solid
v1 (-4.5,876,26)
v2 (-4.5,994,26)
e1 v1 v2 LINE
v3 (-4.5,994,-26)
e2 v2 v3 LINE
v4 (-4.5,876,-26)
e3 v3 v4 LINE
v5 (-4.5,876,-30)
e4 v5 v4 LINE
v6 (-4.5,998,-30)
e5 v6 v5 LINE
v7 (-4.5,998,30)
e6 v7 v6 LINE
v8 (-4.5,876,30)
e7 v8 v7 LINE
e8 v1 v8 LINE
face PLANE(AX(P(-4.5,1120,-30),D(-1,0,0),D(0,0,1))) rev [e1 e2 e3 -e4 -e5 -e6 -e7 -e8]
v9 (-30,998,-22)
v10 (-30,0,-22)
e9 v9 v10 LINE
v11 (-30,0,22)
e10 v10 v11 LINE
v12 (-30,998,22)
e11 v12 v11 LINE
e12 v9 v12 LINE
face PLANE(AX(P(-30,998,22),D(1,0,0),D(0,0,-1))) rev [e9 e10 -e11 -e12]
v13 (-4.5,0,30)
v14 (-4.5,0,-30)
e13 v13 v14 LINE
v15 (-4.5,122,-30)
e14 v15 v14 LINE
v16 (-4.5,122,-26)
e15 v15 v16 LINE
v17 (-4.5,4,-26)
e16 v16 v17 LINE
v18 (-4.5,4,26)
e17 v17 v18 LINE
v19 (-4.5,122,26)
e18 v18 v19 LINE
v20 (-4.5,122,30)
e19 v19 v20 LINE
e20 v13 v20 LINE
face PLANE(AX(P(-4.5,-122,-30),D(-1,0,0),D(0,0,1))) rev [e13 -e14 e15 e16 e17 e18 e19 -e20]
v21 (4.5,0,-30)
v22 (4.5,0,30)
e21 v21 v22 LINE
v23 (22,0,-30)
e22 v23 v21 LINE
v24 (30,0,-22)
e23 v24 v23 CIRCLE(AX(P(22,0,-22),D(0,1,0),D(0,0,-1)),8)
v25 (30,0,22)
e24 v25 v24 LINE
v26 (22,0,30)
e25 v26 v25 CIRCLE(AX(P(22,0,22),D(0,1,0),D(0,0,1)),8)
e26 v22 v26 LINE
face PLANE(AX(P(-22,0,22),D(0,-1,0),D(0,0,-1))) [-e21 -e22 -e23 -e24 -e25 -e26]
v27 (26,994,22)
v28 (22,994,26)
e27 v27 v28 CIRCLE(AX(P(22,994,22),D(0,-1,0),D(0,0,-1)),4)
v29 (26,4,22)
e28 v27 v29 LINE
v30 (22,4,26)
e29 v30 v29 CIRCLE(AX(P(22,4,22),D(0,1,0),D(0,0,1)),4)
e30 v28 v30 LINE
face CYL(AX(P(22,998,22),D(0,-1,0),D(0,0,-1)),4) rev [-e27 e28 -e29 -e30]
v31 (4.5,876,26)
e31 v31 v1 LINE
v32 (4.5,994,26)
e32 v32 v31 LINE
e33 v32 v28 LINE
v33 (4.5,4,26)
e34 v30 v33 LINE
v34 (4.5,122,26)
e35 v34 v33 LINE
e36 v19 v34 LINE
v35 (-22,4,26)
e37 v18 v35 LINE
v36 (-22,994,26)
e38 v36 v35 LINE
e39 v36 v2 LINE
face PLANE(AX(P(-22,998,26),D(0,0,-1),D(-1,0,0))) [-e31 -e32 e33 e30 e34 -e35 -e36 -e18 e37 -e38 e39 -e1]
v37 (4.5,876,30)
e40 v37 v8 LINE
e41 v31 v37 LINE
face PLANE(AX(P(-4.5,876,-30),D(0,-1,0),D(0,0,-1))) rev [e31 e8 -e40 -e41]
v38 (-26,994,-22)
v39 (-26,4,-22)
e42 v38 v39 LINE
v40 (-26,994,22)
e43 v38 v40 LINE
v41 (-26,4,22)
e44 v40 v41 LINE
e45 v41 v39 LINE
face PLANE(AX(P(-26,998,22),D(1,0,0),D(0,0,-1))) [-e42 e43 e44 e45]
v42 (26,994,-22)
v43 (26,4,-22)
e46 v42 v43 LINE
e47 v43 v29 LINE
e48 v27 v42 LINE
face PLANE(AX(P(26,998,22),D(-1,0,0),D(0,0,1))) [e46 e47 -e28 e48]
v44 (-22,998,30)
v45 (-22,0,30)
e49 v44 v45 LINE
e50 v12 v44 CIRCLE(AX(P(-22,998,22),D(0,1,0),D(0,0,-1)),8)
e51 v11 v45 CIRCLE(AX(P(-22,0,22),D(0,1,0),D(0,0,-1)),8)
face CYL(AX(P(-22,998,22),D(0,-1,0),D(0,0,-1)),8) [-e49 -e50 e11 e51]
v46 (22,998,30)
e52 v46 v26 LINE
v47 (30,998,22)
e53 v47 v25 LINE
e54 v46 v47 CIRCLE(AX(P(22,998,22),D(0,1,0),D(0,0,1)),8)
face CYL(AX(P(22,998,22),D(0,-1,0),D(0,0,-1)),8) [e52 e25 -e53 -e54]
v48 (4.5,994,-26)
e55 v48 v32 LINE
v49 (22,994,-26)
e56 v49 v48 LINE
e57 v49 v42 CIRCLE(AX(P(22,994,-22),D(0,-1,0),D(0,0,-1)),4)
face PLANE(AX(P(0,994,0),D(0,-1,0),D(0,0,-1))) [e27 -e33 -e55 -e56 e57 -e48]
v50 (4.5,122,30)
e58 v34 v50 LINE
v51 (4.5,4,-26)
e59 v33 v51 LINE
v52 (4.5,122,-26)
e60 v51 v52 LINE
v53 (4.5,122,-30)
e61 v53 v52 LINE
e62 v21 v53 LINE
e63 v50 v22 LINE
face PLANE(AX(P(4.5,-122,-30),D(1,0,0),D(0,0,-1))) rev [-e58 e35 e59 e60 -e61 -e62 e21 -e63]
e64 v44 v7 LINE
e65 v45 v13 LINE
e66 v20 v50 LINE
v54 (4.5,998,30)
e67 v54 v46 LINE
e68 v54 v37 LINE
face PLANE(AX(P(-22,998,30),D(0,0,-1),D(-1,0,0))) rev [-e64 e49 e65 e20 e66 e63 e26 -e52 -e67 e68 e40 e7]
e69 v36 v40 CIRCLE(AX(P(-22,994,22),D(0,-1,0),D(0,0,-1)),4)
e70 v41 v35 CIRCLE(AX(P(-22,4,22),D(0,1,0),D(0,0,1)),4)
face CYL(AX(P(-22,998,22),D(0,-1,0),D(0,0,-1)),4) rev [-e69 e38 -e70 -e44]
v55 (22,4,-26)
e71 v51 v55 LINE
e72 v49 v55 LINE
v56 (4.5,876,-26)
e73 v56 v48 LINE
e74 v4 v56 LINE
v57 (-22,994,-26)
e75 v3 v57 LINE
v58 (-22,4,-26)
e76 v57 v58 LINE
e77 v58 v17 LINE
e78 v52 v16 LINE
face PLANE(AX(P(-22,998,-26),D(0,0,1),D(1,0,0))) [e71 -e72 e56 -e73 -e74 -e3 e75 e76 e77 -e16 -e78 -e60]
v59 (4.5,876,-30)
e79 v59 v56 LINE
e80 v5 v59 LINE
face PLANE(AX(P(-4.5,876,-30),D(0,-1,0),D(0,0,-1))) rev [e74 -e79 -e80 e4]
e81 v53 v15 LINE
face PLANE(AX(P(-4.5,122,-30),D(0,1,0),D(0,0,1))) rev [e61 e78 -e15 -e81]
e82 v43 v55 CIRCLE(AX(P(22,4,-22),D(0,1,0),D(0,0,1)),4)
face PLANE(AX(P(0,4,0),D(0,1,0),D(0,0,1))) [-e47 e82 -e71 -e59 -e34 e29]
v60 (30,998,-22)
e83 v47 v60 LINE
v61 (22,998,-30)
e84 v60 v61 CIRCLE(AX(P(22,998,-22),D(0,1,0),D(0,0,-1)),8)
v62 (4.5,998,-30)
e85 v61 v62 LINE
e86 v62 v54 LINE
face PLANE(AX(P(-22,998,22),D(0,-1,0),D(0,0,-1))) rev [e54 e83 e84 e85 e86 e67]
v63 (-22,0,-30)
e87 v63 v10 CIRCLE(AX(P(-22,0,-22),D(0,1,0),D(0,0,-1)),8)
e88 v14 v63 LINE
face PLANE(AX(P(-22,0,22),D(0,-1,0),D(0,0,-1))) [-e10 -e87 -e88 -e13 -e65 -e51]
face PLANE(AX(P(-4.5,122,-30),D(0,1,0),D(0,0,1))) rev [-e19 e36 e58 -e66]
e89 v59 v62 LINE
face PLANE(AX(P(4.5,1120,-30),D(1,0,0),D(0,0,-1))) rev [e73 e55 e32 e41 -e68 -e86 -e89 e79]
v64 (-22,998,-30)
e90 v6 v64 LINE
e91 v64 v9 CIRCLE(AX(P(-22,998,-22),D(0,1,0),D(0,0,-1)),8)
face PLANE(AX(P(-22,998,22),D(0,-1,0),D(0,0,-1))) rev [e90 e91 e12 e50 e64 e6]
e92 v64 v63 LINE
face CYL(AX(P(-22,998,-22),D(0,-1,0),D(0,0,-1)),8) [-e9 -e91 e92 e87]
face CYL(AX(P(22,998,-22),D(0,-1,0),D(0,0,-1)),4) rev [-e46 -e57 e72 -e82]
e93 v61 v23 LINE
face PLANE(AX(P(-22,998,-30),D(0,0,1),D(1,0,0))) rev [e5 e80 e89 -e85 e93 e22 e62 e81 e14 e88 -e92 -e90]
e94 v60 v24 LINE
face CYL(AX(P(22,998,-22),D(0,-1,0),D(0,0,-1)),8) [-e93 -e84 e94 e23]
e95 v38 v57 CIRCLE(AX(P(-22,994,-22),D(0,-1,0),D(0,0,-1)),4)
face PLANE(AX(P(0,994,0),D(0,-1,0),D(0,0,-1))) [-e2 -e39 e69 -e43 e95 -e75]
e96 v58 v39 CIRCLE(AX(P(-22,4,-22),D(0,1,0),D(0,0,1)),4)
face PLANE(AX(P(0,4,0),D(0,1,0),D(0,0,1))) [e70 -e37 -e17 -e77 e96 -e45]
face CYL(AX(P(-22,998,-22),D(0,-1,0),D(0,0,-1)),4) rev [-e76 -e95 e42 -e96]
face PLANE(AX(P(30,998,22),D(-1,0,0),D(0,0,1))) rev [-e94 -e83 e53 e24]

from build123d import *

# Parameters (mm, degrees)
BOSS_EXTRUDE1_DEPTH     = 998
CUT_EXTRUDE1_DEPTH      = 1001.251968256
CUT_EXTRUDE1_DEPTH_BACK = 1001.251968256
SKETCH2_W               = 9
SKETCH2_H               = 244
SKETCH3_W               = 21.5
SKETCH3_H               = 52
BOSS_EXTRUDE2_DEPTH     = 4
SKETCH4_W               = 21.5
SKETCH4_H               = 52
BOSS_EXTRUDE3_DEPTH     = 4


with BuildPart() as part:
    # Sketch1 → Boss-Extrude1 (new body)
    with BuildSketch(Plane(origin=(0, 0, 0), x_dir=(1, 0, 0), z_dir=(0, 1, 0))):
        with BuildLine():
            Line((-22, -30), (22, -30))
            ThreePointArc((22, -30), (27.656854249, -27.656854249), (30, -22))
            Line((30, -22), (30, 22))
            ThreePointArc((30, 22), (27.656854249, 27.656854249), (22, 30))
            Line((22, 30), (-22, 30))
            ThreePointArc((-22, 30), (-27.656854249, 27.656854249), (-30, 22))
            Line((-30, 22), (-30, -22))
            ThreePointArc((-30, -22), (-27.656854249, -27.656854249), (-22, -30))
        make_face()
        with BuildLine():
            Line((-22, 26), (22, 26))
            ThreePointArc((22, 26), (24.828427125, 24.828427125), (26, 22))
            Line((26, 22), (26, -22))
            ThreePointArc((26, -22), (24.828427125, -24.828427125), (22, -26))
            Line((22, -26), (-22, -26))
            ThreePointArc((-22, -26), (-24.828427125, -24.828427125), (-26, -22))
            Line((-26, -22), (-26, 22))
            ThreePointArc((-26, 22), (-24.828427125, 24.828427125), (-22, 26))
        make_face(mode=Mode.SUBTRACT)
    extrude(amount=BOSS_EXTRUDE1_DEPTH)

    # Sketch2 → Cut-Extrude1 (cut, two sides: drawn at the far end of the back side and taken through both)
    with BuildSketch(Plane.XY.offset(30).offset(-CUT_EXTRUDE1_DEPTH_BACK)):
        with Locations((0, 998)):
            Rectangle(SKETCH2_W, SKETCH2_H)
        Rectangle(SKETCH2_W, SKETCH2_H)
    extrude(amount=CUT_EXTRUDE1_DEPTH + CUT_EXTRUDE1_DEPTH_BACK, mode=Mode.SUBTRACT)

    # Sketch3 → Boss-Extrude2 (add)
    with BuildSketch(Plane(origin=(0, 998, 0), x_dir=(1, 0, 0), z_dir=(0, 1, 0))):
        with Locations((-15.25, 0)):
            Rectangle(SKETCH3_W, SKETCH3_H)
        with Locations((15.25, 0)):
            Rectangle(SKETCH3_W, SKETCH3_H)
    extrude(amount=-BOSS_EXTRUDE2_DEPTH)

    # Sketch4 → Boss-Extrude3 (add)
    with BuildSketch(Plane.XZ):
        with Locations((-15.25, 0)):
            Rectangle(SKETCH4_W, SKETCH4_H)
        with Locations((15.25, 0)):
            Rectangle(SKETCH4_W, SKETCH4_H)
    extrude(amount=-BOSS_EXTRUDE3_DEPTH)


solid = part.part
